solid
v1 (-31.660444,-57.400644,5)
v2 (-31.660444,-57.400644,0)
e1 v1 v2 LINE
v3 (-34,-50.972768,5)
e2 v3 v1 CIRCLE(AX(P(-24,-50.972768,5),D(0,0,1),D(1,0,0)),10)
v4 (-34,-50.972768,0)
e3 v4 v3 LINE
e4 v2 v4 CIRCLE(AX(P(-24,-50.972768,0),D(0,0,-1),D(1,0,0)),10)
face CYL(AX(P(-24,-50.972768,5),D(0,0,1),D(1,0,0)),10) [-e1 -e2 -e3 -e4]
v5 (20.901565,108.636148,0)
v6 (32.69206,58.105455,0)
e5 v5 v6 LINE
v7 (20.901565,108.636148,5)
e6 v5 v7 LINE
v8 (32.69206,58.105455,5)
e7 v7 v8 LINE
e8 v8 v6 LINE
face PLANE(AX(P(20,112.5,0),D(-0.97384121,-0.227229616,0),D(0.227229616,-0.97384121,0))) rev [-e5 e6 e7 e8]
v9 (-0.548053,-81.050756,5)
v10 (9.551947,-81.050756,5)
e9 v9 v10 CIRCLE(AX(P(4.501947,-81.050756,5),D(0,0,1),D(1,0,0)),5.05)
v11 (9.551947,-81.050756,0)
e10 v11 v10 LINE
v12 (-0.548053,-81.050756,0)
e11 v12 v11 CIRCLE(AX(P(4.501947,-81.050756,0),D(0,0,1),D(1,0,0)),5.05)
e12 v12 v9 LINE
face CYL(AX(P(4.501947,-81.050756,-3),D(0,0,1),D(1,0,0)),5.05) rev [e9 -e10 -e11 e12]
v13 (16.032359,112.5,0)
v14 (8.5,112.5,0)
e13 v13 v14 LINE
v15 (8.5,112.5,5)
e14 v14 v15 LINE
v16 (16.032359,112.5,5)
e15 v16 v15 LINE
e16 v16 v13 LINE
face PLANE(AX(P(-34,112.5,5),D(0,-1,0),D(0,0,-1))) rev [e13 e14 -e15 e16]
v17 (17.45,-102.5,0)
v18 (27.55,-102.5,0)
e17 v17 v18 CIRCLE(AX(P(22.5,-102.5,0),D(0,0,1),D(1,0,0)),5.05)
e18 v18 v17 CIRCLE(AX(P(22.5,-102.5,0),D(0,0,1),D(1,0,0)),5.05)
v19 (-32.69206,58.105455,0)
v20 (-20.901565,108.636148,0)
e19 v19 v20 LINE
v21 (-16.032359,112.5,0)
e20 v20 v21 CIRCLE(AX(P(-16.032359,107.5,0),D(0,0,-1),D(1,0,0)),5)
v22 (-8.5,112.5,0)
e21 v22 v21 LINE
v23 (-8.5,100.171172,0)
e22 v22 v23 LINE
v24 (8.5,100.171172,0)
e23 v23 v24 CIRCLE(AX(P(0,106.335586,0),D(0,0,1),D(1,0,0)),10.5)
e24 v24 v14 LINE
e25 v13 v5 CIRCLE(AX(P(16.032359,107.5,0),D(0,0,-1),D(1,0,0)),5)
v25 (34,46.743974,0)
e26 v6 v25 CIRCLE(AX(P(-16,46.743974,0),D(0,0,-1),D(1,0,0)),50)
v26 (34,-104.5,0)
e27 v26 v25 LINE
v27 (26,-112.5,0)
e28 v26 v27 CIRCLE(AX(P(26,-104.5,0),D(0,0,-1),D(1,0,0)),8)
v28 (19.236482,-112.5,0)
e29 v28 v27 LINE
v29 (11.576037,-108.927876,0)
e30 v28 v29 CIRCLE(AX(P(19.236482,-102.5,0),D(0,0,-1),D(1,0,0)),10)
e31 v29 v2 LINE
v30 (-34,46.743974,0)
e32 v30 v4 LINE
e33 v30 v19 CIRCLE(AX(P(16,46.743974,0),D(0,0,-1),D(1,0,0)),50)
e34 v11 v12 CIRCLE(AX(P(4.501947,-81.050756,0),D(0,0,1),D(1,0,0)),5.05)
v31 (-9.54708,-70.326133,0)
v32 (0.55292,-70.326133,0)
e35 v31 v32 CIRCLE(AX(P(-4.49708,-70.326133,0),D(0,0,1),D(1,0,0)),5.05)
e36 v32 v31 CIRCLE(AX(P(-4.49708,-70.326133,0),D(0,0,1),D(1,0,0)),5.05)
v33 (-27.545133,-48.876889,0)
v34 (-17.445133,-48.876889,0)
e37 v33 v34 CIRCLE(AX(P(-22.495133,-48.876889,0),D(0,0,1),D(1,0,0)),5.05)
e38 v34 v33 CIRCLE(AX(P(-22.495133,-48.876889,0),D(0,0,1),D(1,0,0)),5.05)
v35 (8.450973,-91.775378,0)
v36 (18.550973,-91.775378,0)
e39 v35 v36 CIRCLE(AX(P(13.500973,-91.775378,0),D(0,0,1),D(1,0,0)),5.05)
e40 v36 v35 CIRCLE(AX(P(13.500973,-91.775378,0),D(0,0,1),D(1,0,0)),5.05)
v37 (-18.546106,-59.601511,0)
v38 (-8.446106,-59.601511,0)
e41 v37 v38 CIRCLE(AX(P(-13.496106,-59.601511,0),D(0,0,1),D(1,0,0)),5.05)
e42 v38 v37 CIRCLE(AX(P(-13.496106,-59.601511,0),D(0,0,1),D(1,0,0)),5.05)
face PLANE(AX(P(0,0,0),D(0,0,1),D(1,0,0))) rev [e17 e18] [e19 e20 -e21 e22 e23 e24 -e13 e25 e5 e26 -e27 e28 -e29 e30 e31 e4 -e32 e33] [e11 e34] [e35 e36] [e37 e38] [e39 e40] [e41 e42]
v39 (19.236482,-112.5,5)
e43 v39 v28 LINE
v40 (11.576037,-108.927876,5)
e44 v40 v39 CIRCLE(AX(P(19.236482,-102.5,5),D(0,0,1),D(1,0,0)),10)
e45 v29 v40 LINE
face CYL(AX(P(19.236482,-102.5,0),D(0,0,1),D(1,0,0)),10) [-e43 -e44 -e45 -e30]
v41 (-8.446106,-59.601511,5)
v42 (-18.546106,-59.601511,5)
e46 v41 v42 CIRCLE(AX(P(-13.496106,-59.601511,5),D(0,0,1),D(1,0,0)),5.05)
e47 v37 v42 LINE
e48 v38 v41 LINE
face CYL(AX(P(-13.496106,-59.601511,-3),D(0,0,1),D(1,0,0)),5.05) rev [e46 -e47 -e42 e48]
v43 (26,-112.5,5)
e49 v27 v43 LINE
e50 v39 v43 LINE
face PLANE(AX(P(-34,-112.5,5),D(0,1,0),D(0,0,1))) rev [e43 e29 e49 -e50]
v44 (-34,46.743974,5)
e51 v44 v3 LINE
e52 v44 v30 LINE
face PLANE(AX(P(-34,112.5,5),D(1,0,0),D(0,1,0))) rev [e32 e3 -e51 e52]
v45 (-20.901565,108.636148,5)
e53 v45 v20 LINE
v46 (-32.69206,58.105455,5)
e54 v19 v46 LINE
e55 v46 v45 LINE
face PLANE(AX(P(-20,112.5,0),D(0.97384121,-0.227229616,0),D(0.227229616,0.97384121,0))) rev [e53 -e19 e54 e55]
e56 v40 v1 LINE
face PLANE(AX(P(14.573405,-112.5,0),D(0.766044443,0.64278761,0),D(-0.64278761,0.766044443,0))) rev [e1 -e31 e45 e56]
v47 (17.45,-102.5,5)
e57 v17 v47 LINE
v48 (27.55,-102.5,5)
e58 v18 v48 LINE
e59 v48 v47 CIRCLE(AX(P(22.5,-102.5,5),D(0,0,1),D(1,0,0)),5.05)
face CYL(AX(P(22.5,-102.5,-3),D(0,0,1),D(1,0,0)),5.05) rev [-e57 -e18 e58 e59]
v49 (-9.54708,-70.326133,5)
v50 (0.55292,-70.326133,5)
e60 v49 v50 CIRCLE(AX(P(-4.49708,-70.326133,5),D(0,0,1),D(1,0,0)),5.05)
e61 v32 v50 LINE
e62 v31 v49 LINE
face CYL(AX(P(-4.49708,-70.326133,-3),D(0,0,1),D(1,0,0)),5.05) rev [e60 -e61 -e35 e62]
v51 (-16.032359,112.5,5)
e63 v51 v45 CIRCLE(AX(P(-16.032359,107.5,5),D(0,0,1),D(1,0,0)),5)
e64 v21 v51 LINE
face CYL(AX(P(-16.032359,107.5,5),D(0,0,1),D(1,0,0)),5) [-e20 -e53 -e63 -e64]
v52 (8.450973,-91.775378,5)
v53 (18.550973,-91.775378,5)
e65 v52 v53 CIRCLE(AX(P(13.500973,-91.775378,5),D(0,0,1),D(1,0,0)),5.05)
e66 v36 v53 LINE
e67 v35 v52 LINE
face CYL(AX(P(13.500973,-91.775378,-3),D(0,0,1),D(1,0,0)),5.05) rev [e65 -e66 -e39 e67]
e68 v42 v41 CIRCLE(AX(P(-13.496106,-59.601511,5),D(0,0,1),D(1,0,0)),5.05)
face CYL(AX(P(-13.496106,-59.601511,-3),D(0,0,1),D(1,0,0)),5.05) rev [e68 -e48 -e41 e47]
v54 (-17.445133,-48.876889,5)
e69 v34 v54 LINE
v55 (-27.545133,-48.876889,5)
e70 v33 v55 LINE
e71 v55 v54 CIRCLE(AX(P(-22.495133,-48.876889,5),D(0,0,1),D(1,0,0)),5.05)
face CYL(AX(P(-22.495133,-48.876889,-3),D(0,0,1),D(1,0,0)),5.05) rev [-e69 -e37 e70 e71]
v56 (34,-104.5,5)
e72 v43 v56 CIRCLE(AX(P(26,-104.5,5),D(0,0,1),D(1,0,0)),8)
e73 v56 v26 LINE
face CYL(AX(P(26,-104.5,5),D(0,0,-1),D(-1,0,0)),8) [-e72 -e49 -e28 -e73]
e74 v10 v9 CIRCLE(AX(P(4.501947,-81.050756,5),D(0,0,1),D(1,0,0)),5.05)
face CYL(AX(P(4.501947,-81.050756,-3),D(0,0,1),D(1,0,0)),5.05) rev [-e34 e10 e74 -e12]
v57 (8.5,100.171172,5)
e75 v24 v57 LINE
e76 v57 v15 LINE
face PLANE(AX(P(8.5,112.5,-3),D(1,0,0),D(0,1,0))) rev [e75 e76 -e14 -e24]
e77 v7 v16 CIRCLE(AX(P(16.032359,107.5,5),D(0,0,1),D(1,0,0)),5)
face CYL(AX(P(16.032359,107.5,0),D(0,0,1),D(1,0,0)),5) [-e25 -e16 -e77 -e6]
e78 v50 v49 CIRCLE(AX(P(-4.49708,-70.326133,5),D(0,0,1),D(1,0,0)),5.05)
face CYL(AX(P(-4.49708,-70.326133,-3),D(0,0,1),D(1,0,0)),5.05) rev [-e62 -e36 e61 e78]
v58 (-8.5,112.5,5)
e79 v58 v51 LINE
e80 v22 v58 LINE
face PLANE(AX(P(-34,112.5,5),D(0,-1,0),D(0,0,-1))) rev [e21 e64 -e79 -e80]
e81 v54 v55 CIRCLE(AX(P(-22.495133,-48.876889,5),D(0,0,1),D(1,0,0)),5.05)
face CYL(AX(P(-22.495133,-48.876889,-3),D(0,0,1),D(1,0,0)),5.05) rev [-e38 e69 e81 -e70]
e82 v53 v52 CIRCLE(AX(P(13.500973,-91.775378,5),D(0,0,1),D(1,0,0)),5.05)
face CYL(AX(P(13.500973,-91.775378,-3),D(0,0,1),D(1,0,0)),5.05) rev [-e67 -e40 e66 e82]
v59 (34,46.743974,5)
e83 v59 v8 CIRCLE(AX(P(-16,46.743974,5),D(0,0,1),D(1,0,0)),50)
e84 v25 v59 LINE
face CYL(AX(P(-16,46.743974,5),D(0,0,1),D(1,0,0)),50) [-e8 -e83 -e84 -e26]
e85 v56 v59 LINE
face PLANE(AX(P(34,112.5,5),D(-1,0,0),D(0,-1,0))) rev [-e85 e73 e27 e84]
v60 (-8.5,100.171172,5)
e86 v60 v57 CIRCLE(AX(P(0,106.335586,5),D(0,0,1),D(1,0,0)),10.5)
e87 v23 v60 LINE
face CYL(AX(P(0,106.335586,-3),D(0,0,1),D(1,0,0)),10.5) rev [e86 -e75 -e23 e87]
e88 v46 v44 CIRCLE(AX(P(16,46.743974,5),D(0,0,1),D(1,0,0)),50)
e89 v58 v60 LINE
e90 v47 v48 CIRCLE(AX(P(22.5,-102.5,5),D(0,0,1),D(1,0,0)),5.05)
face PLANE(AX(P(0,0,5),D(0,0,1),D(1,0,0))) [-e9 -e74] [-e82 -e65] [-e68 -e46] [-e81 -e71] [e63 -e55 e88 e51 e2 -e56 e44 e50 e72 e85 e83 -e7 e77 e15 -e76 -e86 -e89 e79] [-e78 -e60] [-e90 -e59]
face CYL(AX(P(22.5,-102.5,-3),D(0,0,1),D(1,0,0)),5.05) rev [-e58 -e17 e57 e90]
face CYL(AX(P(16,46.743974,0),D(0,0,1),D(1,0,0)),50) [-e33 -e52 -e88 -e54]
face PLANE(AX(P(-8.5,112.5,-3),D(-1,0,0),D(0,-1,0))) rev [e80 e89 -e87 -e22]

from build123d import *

# Parameters (mm, degrees)
SKETCH1_W           = 68
SKETCH1_H           = 225
BOSS_EXTRUDE1_DEPTH = 5
SKETCH3_R           = 5.05
CUT_EXTRUDE1_DEPTH  = 8
FILLET1_R           = 8
CUT_EXTRUDE2_DEPTH  = 118.631840928
FILLET2_R           = 10
CUT_EXTRUDE3_DEPTH  = 8
FILLET3_R           = 10
CUT_EXTRUDE4_DEPTH  = 118.631840928
FILLET4_R           = 5
FILLET5_R           = 50


with BuildPart() as part:
    # Sketch1 → Boss-Extrude1 (new body)
    with BuildSketch(Plane.XY):
        Rectangle(SKETCH1_W, SKETCH1_H)
    extrude(amount=BOSS_EXTRUDE1_DEPTH)

    # Sketch3 → Cut-Extrude1 (cut)
    with BuildSketch(Plane.XY.offset(5)):
        with Locations((22.5, -102.5)):
            Circle(SKETCH3_R)
        with Locations((13.500973464, -91.775377796)):
            Circle(SKETCH3_R)
        with Locations((4.501946929, -81.050755593)):
            Circle(SKETCH3_R)
        with Locations((-4.497079607, -70.326133389)):
            Circle(SKETCH3_R)
        with Locations((-13.496106142, -59.601511185)):
            Circle(SKETCH3_R)
        with Locations((-22.495132678, -48.876888982)):
            Circle(SKETCH3_R)
    extrude(amount=-CUT_EXTRUDE1_DEPTH, mode=Mode.SUBTRACT)

    # Fillet1
    fillet1_edges = [part.edges().sort_by_distance(p)[0] for p in [
        (34, -112.5, 2.5),
    ]]
    fillet(fillet1_edges, radius=FILLET1_R)

    # Sketch5 → Cut-Extrude2 (cut, through all)
    with BuildSketch(Plane.XY.offset(5)):
        Polygon((14.573405195, -112.5), (-34, -54.612469854), (-34, -112.5), align=None)
    extrude(amount=-CUT_EXTRUDE2_DEPTH, mode=Mode.SUBTRACT)

    # Fillet2
    fillet2_edges = [part.edges().sort_by_distance(p)[0] for p in [
        (14.573405195, -112.5, 2.5),
    ]]
    fillet(fillet2_edges, radius=FILLET2_R)

    # Sketch6 → Cut-Extrude3 (cut)
    with BuildSketch(Plane.XY.offset(5)):
        with BuildLine():
            Line((-8.5, 112.5), (-8.5, 100.171171994))
            ThreePointArc((-8.5, 100.171171994), (0, 95.835585997), (8.5, 100.171171994))
            Line((8.5, 100.171171994), (8.5, 112.5))
            ThreePointArc((8.5, 112.5), (0, 116.835585997), (-8.5, 112.5))
        make_face()
    extrude(amount=-CUT_EXTRUDE3_DEPTH, mode=Mode.SUBTRACT)

    # Fillet3
    fillet3_edges = [part.edges().sort_by_distance(p)[0] for p in [
        (-34, -54.612469854, 2.5),
    ]]
    fillet(fillet3_edges, radius=FILLET3_R)

    # Sketch7 → Cut-Extrude4 (cut, through all)
    with BuildSketch(Plane.XY.offset(5)):
        Polygon((-20, 112.5), (-34, 52.5), (-34, 112.5), align=None)
        Polygon((34, 112.5), (20, 112.5), (34, 52.5), align=None)
    extrude(amount=-CUT_EXTRUDE4_DEPTH, mode=Mode.SUBTRACT)

    # Fillet4
    fillet4_edges = [part.edges().sort_by_distance(p)[0] for p in [
        (-20, 112.5, 2.5),
        (20, 112.5, 2.5),
    ]]
    fillet(fillet4_edges, radius=FILLET4_R)

    # Fillet5
    fillet5_edges = [part.edges().sort_by_distance(p)[0] for p in [
        (-34, 52.5, 2.5),
        (34, 52.5, 2.5),
    ]]
    fillet(fillet5_edges, radius=FILLET5_R)


solid = part.part
